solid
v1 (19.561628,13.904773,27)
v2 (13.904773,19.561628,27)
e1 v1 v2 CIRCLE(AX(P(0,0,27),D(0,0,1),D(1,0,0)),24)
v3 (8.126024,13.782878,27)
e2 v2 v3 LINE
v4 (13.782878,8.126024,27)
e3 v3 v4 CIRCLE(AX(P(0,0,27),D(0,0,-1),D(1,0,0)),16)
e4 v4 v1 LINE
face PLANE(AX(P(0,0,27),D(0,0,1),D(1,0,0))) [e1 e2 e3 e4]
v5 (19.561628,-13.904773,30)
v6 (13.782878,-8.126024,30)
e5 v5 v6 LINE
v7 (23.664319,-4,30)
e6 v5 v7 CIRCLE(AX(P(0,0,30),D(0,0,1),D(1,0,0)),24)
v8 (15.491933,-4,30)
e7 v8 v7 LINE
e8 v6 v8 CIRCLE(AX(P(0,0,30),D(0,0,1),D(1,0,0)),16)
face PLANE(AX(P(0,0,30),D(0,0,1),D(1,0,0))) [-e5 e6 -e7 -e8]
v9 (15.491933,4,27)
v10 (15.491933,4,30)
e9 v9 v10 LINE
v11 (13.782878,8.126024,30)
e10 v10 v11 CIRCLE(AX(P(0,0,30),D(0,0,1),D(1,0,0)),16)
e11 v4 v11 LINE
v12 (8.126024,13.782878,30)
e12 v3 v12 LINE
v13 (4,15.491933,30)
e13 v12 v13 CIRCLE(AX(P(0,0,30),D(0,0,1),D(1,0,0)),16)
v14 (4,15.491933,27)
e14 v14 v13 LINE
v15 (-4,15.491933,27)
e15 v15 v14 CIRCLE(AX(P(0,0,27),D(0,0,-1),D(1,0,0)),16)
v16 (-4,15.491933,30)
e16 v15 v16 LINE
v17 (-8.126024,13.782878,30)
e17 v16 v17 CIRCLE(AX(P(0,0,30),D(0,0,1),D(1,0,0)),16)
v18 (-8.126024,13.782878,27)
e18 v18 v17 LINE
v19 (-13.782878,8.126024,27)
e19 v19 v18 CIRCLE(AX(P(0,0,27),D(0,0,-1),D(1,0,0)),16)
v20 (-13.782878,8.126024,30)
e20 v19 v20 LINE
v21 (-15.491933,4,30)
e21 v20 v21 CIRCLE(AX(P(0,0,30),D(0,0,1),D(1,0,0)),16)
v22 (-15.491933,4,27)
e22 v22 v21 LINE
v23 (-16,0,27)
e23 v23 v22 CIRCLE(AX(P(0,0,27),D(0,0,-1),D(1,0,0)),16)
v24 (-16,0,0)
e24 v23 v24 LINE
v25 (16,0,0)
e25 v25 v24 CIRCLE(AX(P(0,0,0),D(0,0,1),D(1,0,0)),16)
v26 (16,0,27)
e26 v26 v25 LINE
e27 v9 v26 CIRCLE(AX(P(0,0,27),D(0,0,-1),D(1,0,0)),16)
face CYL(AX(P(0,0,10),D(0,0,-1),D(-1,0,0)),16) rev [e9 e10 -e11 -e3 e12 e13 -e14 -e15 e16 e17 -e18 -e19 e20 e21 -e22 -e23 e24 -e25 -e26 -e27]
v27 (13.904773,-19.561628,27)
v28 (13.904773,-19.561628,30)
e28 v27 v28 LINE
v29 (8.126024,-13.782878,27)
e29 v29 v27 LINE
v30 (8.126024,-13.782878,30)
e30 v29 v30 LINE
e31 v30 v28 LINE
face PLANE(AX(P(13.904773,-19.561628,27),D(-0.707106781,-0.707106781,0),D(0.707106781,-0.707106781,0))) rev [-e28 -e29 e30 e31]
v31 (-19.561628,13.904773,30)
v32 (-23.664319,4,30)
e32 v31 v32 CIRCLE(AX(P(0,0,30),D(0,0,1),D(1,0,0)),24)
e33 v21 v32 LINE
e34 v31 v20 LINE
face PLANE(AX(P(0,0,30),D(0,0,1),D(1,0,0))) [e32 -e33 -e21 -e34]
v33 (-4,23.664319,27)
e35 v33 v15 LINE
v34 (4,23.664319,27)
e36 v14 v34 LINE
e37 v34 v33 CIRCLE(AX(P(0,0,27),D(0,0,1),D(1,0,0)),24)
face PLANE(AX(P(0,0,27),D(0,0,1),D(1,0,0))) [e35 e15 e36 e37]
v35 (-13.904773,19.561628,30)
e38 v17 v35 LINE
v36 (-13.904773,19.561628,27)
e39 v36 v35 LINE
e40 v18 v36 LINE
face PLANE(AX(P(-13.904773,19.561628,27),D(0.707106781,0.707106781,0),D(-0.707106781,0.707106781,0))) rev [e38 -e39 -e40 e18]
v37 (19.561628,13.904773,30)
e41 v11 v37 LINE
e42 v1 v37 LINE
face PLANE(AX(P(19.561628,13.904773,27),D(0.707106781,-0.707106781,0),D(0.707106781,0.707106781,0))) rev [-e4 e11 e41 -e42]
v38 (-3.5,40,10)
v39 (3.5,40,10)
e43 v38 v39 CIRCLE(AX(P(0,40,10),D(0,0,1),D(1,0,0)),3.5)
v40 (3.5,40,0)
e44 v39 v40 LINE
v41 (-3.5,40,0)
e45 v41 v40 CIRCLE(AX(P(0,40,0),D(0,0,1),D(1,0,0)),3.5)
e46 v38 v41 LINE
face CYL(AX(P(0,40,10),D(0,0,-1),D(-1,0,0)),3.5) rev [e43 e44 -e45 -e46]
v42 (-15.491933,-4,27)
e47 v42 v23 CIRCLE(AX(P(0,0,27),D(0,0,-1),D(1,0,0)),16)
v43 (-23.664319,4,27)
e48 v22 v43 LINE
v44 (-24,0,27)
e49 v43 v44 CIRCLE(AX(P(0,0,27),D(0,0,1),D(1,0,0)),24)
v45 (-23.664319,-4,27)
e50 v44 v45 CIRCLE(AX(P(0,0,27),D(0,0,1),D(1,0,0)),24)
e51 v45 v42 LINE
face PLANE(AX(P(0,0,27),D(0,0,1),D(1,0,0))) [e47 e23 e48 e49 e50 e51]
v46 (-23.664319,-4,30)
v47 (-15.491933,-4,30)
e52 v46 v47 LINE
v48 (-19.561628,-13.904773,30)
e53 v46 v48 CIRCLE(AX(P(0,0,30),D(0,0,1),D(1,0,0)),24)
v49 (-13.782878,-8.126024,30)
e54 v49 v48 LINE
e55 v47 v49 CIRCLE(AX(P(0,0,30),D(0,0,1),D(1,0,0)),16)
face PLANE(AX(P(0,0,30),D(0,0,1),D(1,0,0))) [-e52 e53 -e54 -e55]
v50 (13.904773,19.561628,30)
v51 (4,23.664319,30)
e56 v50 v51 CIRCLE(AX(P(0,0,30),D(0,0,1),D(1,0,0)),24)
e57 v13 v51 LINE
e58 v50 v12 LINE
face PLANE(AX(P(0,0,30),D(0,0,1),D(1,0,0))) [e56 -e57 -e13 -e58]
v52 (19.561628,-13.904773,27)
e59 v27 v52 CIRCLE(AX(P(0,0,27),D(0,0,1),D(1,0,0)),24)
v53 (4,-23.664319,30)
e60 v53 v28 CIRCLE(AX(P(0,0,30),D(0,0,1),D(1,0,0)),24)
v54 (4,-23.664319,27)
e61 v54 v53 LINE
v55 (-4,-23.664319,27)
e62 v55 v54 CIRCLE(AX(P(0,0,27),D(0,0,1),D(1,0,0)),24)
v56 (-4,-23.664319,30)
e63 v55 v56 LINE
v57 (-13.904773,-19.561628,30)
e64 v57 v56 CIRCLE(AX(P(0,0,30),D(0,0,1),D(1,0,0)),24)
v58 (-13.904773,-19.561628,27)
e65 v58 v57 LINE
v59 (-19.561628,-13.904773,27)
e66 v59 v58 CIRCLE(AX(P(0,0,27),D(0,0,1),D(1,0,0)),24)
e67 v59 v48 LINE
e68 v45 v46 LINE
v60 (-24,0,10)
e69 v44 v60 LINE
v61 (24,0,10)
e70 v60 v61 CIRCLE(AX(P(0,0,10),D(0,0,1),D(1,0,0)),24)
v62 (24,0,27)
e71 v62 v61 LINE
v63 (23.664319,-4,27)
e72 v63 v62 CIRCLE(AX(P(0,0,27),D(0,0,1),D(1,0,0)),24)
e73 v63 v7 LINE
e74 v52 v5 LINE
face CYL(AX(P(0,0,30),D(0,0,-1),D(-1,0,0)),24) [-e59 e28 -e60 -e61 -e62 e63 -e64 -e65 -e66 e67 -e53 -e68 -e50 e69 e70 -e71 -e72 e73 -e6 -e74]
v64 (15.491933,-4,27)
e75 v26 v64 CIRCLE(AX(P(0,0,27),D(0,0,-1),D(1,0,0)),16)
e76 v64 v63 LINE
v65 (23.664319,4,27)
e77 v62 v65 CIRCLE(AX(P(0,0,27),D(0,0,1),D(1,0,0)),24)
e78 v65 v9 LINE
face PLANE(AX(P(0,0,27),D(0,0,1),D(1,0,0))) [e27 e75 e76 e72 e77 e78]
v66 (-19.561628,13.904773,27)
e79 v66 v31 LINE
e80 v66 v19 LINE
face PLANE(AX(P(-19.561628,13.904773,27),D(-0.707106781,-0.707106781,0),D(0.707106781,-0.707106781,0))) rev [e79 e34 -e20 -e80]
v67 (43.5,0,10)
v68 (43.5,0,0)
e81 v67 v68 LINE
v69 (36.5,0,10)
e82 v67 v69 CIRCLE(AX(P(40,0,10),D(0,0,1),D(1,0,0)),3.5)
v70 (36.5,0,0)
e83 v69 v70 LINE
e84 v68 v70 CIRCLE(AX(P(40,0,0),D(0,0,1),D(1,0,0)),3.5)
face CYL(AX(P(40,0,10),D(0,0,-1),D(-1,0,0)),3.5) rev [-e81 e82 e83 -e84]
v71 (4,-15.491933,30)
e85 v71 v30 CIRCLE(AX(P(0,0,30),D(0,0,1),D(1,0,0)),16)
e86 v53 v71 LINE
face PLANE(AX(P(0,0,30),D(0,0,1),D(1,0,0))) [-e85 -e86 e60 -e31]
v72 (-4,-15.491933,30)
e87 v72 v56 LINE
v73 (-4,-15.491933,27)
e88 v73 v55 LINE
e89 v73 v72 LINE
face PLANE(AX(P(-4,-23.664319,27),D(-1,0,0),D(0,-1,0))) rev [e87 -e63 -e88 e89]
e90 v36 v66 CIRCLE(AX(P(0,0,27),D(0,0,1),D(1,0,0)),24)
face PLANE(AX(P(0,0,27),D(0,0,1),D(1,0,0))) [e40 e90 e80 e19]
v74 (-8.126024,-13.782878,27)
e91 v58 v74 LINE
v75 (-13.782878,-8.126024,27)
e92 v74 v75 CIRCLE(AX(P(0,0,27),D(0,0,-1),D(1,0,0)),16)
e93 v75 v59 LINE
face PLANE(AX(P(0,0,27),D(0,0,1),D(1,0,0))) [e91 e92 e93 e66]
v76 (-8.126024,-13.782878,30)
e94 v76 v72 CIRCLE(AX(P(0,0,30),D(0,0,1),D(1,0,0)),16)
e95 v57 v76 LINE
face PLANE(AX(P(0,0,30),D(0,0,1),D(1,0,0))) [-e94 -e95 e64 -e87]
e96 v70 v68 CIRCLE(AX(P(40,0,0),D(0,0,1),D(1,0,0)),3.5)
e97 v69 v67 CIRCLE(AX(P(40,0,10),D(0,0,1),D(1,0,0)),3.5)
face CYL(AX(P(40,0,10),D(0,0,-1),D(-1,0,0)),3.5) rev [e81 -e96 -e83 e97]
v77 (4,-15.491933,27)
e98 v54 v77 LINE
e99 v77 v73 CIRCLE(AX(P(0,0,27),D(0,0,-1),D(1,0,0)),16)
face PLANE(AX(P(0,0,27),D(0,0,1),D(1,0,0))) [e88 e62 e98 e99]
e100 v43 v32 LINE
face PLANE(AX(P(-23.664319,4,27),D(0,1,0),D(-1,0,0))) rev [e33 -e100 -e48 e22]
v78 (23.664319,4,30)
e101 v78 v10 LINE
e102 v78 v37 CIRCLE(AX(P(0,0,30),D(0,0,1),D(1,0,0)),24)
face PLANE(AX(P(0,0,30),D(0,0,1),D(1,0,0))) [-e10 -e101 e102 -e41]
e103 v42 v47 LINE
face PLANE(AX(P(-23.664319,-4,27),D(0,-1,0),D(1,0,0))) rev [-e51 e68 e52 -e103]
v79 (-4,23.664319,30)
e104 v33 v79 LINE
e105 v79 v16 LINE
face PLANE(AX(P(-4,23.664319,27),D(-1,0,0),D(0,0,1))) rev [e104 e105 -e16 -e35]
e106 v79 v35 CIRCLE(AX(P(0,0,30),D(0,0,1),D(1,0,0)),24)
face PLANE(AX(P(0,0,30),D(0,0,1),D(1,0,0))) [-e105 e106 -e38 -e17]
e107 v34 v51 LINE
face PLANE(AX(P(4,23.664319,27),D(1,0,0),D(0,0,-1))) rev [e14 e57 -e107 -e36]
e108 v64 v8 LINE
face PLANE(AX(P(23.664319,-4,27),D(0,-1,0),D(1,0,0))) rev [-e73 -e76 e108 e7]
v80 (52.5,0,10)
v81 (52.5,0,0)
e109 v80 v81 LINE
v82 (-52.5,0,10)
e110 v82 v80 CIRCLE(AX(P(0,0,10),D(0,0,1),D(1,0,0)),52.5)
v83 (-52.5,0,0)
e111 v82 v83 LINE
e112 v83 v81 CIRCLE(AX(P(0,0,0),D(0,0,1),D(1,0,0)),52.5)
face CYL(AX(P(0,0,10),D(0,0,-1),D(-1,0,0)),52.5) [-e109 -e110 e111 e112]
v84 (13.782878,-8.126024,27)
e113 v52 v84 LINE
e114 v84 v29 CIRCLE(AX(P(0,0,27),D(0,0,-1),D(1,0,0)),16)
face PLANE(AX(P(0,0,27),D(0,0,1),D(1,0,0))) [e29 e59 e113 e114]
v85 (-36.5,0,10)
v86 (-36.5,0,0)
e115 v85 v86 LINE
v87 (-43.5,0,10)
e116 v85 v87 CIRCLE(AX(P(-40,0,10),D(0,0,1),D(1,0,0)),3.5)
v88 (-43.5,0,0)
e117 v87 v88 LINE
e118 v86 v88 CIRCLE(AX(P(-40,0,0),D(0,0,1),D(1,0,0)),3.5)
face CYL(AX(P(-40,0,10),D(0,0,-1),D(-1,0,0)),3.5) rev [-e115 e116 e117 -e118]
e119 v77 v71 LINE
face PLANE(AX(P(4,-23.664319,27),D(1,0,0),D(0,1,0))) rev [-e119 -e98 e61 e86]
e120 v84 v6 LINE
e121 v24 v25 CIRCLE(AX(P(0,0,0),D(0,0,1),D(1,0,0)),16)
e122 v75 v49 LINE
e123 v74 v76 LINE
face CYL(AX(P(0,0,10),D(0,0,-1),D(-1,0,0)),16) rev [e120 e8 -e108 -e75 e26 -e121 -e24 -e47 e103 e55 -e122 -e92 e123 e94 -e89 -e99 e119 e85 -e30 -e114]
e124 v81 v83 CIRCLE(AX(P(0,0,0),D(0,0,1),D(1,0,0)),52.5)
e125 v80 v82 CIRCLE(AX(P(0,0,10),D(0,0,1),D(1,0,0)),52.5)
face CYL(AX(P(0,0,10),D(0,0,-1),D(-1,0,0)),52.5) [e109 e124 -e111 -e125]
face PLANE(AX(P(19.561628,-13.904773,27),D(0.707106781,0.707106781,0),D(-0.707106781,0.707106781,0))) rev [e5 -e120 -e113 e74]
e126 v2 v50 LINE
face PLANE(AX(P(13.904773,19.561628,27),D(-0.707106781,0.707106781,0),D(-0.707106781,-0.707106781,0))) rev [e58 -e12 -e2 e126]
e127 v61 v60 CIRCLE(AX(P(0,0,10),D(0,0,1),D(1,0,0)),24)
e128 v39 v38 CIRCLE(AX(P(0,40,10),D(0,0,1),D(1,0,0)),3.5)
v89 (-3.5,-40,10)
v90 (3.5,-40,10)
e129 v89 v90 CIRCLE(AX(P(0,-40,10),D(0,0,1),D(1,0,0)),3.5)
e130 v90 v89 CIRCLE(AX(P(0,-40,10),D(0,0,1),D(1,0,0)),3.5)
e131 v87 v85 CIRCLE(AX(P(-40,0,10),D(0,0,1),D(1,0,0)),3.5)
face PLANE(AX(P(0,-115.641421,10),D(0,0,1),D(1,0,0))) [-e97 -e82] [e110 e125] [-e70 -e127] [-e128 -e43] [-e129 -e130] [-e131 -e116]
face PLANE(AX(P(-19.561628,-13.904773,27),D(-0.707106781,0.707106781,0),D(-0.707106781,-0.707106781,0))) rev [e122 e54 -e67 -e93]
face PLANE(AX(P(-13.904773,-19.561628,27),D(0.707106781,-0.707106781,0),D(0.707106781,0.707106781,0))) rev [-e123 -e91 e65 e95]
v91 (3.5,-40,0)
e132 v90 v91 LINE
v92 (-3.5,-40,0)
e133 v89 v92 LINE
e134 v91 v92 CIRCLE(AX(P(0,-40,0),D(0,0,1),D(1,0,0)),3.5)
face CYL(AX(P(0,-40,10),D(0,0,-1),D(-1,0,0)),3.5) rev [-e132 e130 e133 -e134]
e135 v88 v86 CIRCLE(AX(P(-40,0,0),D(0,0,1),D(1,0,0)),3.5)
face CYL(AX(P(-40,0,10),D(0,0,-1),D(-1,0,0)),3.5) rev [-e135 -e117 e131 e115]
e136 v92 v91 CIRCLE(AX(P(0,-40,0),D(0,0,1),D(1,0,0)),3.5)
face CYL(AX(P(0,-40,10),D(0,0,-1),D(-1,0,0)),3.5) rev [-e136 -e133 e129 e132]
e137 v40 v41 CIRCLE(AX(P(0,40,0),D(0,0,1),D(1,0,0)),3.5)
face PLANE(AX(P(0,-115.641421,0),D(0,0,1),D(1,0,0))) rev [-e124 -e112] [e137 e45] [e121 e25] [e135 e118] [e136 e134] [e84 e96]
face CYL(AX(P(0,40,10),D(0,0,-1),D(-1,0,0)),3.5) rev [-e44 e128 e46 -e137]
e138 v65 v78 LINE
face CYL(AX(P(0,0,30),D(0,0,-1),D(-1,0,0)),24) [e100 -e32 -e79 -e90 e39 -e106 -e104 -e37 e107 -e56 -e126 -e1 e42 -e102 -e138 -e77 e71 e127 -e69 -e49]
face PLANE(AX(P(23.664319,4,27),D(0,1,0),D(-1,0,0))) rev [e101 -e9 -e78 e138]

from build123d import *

# Parameters (mm, degrees)
SKETCH_1_R          = 52.5
SKETCH_1_R_2        = 16
SKETCH_1_R_3        = 3.5
EXTRUDE_1_DEPTH     = 10
SKETCH_2_R          = 24
SKETCH_2_R_2        = 16
EXTRUDE_2_DEPTH     = 20
CUT_EXTRUDE_START   = -3
CUT_EXTRUDE_2_DEPTH = 3


with BuildPart() as part:
    # 草图1 → 凸台-拉伸1 (new body)
    with BuildSketch(Plane.XY):
        Circle(SKETCH_1_R)
        Circle(SKETCH_1_R_2, mode=Mode.SUBTRACT)
        with Locations((0, 40)):
            Circle(SKETCH_1_R_3, mode=Mode.SUBTRACT)
        with Locations((40, 0)):
            Circle(SKETCH_1_R_3, mode=Mode.SUBTRACT)
        with Locations((0, -40)):
            Circle(SKETCH_1_R_3, mode=Mode.SUBTRACT)
        with Locations((-40, 0)):
            Circle(SKETCH_1_R_3, mode=Mode.SUBTRACT)
    extrude(amount=EXTRUDE_1_DEPTH)

    # 草图2 → 凸台-拉伸2 (add)
    with BuildSketch(Plane.XY.offset(10)):
        Circle(SKETCH_2_R)
        Circle(SKETCH_2_R_2, mode=Mode.SUBTRACT)
    extrude(amount=EXTRUDE_2_DEPTH)

    # 草图3 → 切除-拉伸2 (cut)
    with BuildSketch(Plane.XY.offset(30).offset(CUT_EXTRUDE_START)):
        with BuildLine():
            Line((-4, 23.664319132), (-4, 15.491933385))
            ThreePointArc((-4, 15.491933385), (0, 16), (4, 15.491933385))
            Line((4, 15.491933385), (4, 23.664319132))
            ThreePointArc((4, 23.664319132), (0, 24), (-4, 23.664319132))
        make_face()
        with BuildLine():
            Line((13.904773406, 19.561627655), (8.126024025, 13.782878275))
            ThreePointArc((8.126024025, 13.782878275), (11.313708499, 11.313708499), (13.782878275, 8.126024025))
            Line((13.782878275, 8.126024025), (19.561627655, 13.904773406))
            ThreePointArc((19.561627655, 13.904773406), (16.970562748, 16.970562748), (13.904773406, 19.561627655))
        make_face()
        with BuildLine():
            Line((23.664319132, 4), (15.491933385, 4))
            ThreePointArc((15.491933385, 4), (16, 0), (15.491933385, -4))
            Line((15.491933385, -4), (23.664319132, -4))
            ThreePointArc((23.664319132, -4), (24, 0), (23.664319132, 4))
        make_face()
        with BuildLine():
            Line((19.561627655, -13.904773406), (13.782878275, -8.126024025))
            ThreePointArc((13.782878275, -8.126024025), (11.313708499, -11.313708499), (8.126024025, -13.782878275))
            Line((8.126024025, -13.782878275), (13.904773406, -19.561627655))
            ThreePointArc((13.904773406, -19.561627655), (16.970562748, -16.970562748), (19.561627655, -13.904773406))
        make_face()
        with BuildLine():
            Line((4, -23.664319132), (4, -15.491933385))
            ThreePointArc((4, -15.491933385), (0, -16), (-4, -15.491933385))
            Line((-4, -15.491933385), (-4, -23.664319132))
            ThreePointArc((-4, -23.664319132), (0, -24), (4, -23.664319132))
        make_face()
        with BuildLine():
            Line((-13.904773406, -19.561627655), (-8.126024025, -13.782878275))
            ThreePointArc((-8.126024025, -13.782878275), (-11.313708499, -11.313708499), (-13.782878275, -8.126024025))
            Line((-13.782878275, -8.126024025), (-19.561627655, -13.904773406))
            ThreePointArc((-19.561627655, -13.904773406), (-16.970562748, -16.970562748), (-13.904773406, -19.561627655))
        make_face()
        with BuildLine():
            Line((-23.664319132, -4), (-15.491933385, -4))
            ThreePointArc((-15.491933385, -4), (-16, 0), (-15.491933385, 4))
            Line((-15.491933385, 4), (-23.664319132, 4))
            ThreePointArc((-23.664319132, 4), (-24, 0), (-23.664319132, -4))
        make_face()
        with BuildLine():
            Line((-19.561627655, 13.904773406), (-13.782878275, 8.126024025))
            ThreePointArc((-13.782878275, 8.126024025), (-11.313708499, 11.313708499), (-8.126024025, 13.782878275))
            Line((-8.126024025, 13.782878275), (-13.904773406, 19.561627655))
            ThreePointArc((-13.904773406, 19.561627655), (-16.970562748, 16.970562748), (-19.561627655, 13.904773406))
        make_face()
    extrude(amount=CUT_EXTRUDE_2_DEPTH, mode=Mode.SUBTRACT)


solid = part.part
